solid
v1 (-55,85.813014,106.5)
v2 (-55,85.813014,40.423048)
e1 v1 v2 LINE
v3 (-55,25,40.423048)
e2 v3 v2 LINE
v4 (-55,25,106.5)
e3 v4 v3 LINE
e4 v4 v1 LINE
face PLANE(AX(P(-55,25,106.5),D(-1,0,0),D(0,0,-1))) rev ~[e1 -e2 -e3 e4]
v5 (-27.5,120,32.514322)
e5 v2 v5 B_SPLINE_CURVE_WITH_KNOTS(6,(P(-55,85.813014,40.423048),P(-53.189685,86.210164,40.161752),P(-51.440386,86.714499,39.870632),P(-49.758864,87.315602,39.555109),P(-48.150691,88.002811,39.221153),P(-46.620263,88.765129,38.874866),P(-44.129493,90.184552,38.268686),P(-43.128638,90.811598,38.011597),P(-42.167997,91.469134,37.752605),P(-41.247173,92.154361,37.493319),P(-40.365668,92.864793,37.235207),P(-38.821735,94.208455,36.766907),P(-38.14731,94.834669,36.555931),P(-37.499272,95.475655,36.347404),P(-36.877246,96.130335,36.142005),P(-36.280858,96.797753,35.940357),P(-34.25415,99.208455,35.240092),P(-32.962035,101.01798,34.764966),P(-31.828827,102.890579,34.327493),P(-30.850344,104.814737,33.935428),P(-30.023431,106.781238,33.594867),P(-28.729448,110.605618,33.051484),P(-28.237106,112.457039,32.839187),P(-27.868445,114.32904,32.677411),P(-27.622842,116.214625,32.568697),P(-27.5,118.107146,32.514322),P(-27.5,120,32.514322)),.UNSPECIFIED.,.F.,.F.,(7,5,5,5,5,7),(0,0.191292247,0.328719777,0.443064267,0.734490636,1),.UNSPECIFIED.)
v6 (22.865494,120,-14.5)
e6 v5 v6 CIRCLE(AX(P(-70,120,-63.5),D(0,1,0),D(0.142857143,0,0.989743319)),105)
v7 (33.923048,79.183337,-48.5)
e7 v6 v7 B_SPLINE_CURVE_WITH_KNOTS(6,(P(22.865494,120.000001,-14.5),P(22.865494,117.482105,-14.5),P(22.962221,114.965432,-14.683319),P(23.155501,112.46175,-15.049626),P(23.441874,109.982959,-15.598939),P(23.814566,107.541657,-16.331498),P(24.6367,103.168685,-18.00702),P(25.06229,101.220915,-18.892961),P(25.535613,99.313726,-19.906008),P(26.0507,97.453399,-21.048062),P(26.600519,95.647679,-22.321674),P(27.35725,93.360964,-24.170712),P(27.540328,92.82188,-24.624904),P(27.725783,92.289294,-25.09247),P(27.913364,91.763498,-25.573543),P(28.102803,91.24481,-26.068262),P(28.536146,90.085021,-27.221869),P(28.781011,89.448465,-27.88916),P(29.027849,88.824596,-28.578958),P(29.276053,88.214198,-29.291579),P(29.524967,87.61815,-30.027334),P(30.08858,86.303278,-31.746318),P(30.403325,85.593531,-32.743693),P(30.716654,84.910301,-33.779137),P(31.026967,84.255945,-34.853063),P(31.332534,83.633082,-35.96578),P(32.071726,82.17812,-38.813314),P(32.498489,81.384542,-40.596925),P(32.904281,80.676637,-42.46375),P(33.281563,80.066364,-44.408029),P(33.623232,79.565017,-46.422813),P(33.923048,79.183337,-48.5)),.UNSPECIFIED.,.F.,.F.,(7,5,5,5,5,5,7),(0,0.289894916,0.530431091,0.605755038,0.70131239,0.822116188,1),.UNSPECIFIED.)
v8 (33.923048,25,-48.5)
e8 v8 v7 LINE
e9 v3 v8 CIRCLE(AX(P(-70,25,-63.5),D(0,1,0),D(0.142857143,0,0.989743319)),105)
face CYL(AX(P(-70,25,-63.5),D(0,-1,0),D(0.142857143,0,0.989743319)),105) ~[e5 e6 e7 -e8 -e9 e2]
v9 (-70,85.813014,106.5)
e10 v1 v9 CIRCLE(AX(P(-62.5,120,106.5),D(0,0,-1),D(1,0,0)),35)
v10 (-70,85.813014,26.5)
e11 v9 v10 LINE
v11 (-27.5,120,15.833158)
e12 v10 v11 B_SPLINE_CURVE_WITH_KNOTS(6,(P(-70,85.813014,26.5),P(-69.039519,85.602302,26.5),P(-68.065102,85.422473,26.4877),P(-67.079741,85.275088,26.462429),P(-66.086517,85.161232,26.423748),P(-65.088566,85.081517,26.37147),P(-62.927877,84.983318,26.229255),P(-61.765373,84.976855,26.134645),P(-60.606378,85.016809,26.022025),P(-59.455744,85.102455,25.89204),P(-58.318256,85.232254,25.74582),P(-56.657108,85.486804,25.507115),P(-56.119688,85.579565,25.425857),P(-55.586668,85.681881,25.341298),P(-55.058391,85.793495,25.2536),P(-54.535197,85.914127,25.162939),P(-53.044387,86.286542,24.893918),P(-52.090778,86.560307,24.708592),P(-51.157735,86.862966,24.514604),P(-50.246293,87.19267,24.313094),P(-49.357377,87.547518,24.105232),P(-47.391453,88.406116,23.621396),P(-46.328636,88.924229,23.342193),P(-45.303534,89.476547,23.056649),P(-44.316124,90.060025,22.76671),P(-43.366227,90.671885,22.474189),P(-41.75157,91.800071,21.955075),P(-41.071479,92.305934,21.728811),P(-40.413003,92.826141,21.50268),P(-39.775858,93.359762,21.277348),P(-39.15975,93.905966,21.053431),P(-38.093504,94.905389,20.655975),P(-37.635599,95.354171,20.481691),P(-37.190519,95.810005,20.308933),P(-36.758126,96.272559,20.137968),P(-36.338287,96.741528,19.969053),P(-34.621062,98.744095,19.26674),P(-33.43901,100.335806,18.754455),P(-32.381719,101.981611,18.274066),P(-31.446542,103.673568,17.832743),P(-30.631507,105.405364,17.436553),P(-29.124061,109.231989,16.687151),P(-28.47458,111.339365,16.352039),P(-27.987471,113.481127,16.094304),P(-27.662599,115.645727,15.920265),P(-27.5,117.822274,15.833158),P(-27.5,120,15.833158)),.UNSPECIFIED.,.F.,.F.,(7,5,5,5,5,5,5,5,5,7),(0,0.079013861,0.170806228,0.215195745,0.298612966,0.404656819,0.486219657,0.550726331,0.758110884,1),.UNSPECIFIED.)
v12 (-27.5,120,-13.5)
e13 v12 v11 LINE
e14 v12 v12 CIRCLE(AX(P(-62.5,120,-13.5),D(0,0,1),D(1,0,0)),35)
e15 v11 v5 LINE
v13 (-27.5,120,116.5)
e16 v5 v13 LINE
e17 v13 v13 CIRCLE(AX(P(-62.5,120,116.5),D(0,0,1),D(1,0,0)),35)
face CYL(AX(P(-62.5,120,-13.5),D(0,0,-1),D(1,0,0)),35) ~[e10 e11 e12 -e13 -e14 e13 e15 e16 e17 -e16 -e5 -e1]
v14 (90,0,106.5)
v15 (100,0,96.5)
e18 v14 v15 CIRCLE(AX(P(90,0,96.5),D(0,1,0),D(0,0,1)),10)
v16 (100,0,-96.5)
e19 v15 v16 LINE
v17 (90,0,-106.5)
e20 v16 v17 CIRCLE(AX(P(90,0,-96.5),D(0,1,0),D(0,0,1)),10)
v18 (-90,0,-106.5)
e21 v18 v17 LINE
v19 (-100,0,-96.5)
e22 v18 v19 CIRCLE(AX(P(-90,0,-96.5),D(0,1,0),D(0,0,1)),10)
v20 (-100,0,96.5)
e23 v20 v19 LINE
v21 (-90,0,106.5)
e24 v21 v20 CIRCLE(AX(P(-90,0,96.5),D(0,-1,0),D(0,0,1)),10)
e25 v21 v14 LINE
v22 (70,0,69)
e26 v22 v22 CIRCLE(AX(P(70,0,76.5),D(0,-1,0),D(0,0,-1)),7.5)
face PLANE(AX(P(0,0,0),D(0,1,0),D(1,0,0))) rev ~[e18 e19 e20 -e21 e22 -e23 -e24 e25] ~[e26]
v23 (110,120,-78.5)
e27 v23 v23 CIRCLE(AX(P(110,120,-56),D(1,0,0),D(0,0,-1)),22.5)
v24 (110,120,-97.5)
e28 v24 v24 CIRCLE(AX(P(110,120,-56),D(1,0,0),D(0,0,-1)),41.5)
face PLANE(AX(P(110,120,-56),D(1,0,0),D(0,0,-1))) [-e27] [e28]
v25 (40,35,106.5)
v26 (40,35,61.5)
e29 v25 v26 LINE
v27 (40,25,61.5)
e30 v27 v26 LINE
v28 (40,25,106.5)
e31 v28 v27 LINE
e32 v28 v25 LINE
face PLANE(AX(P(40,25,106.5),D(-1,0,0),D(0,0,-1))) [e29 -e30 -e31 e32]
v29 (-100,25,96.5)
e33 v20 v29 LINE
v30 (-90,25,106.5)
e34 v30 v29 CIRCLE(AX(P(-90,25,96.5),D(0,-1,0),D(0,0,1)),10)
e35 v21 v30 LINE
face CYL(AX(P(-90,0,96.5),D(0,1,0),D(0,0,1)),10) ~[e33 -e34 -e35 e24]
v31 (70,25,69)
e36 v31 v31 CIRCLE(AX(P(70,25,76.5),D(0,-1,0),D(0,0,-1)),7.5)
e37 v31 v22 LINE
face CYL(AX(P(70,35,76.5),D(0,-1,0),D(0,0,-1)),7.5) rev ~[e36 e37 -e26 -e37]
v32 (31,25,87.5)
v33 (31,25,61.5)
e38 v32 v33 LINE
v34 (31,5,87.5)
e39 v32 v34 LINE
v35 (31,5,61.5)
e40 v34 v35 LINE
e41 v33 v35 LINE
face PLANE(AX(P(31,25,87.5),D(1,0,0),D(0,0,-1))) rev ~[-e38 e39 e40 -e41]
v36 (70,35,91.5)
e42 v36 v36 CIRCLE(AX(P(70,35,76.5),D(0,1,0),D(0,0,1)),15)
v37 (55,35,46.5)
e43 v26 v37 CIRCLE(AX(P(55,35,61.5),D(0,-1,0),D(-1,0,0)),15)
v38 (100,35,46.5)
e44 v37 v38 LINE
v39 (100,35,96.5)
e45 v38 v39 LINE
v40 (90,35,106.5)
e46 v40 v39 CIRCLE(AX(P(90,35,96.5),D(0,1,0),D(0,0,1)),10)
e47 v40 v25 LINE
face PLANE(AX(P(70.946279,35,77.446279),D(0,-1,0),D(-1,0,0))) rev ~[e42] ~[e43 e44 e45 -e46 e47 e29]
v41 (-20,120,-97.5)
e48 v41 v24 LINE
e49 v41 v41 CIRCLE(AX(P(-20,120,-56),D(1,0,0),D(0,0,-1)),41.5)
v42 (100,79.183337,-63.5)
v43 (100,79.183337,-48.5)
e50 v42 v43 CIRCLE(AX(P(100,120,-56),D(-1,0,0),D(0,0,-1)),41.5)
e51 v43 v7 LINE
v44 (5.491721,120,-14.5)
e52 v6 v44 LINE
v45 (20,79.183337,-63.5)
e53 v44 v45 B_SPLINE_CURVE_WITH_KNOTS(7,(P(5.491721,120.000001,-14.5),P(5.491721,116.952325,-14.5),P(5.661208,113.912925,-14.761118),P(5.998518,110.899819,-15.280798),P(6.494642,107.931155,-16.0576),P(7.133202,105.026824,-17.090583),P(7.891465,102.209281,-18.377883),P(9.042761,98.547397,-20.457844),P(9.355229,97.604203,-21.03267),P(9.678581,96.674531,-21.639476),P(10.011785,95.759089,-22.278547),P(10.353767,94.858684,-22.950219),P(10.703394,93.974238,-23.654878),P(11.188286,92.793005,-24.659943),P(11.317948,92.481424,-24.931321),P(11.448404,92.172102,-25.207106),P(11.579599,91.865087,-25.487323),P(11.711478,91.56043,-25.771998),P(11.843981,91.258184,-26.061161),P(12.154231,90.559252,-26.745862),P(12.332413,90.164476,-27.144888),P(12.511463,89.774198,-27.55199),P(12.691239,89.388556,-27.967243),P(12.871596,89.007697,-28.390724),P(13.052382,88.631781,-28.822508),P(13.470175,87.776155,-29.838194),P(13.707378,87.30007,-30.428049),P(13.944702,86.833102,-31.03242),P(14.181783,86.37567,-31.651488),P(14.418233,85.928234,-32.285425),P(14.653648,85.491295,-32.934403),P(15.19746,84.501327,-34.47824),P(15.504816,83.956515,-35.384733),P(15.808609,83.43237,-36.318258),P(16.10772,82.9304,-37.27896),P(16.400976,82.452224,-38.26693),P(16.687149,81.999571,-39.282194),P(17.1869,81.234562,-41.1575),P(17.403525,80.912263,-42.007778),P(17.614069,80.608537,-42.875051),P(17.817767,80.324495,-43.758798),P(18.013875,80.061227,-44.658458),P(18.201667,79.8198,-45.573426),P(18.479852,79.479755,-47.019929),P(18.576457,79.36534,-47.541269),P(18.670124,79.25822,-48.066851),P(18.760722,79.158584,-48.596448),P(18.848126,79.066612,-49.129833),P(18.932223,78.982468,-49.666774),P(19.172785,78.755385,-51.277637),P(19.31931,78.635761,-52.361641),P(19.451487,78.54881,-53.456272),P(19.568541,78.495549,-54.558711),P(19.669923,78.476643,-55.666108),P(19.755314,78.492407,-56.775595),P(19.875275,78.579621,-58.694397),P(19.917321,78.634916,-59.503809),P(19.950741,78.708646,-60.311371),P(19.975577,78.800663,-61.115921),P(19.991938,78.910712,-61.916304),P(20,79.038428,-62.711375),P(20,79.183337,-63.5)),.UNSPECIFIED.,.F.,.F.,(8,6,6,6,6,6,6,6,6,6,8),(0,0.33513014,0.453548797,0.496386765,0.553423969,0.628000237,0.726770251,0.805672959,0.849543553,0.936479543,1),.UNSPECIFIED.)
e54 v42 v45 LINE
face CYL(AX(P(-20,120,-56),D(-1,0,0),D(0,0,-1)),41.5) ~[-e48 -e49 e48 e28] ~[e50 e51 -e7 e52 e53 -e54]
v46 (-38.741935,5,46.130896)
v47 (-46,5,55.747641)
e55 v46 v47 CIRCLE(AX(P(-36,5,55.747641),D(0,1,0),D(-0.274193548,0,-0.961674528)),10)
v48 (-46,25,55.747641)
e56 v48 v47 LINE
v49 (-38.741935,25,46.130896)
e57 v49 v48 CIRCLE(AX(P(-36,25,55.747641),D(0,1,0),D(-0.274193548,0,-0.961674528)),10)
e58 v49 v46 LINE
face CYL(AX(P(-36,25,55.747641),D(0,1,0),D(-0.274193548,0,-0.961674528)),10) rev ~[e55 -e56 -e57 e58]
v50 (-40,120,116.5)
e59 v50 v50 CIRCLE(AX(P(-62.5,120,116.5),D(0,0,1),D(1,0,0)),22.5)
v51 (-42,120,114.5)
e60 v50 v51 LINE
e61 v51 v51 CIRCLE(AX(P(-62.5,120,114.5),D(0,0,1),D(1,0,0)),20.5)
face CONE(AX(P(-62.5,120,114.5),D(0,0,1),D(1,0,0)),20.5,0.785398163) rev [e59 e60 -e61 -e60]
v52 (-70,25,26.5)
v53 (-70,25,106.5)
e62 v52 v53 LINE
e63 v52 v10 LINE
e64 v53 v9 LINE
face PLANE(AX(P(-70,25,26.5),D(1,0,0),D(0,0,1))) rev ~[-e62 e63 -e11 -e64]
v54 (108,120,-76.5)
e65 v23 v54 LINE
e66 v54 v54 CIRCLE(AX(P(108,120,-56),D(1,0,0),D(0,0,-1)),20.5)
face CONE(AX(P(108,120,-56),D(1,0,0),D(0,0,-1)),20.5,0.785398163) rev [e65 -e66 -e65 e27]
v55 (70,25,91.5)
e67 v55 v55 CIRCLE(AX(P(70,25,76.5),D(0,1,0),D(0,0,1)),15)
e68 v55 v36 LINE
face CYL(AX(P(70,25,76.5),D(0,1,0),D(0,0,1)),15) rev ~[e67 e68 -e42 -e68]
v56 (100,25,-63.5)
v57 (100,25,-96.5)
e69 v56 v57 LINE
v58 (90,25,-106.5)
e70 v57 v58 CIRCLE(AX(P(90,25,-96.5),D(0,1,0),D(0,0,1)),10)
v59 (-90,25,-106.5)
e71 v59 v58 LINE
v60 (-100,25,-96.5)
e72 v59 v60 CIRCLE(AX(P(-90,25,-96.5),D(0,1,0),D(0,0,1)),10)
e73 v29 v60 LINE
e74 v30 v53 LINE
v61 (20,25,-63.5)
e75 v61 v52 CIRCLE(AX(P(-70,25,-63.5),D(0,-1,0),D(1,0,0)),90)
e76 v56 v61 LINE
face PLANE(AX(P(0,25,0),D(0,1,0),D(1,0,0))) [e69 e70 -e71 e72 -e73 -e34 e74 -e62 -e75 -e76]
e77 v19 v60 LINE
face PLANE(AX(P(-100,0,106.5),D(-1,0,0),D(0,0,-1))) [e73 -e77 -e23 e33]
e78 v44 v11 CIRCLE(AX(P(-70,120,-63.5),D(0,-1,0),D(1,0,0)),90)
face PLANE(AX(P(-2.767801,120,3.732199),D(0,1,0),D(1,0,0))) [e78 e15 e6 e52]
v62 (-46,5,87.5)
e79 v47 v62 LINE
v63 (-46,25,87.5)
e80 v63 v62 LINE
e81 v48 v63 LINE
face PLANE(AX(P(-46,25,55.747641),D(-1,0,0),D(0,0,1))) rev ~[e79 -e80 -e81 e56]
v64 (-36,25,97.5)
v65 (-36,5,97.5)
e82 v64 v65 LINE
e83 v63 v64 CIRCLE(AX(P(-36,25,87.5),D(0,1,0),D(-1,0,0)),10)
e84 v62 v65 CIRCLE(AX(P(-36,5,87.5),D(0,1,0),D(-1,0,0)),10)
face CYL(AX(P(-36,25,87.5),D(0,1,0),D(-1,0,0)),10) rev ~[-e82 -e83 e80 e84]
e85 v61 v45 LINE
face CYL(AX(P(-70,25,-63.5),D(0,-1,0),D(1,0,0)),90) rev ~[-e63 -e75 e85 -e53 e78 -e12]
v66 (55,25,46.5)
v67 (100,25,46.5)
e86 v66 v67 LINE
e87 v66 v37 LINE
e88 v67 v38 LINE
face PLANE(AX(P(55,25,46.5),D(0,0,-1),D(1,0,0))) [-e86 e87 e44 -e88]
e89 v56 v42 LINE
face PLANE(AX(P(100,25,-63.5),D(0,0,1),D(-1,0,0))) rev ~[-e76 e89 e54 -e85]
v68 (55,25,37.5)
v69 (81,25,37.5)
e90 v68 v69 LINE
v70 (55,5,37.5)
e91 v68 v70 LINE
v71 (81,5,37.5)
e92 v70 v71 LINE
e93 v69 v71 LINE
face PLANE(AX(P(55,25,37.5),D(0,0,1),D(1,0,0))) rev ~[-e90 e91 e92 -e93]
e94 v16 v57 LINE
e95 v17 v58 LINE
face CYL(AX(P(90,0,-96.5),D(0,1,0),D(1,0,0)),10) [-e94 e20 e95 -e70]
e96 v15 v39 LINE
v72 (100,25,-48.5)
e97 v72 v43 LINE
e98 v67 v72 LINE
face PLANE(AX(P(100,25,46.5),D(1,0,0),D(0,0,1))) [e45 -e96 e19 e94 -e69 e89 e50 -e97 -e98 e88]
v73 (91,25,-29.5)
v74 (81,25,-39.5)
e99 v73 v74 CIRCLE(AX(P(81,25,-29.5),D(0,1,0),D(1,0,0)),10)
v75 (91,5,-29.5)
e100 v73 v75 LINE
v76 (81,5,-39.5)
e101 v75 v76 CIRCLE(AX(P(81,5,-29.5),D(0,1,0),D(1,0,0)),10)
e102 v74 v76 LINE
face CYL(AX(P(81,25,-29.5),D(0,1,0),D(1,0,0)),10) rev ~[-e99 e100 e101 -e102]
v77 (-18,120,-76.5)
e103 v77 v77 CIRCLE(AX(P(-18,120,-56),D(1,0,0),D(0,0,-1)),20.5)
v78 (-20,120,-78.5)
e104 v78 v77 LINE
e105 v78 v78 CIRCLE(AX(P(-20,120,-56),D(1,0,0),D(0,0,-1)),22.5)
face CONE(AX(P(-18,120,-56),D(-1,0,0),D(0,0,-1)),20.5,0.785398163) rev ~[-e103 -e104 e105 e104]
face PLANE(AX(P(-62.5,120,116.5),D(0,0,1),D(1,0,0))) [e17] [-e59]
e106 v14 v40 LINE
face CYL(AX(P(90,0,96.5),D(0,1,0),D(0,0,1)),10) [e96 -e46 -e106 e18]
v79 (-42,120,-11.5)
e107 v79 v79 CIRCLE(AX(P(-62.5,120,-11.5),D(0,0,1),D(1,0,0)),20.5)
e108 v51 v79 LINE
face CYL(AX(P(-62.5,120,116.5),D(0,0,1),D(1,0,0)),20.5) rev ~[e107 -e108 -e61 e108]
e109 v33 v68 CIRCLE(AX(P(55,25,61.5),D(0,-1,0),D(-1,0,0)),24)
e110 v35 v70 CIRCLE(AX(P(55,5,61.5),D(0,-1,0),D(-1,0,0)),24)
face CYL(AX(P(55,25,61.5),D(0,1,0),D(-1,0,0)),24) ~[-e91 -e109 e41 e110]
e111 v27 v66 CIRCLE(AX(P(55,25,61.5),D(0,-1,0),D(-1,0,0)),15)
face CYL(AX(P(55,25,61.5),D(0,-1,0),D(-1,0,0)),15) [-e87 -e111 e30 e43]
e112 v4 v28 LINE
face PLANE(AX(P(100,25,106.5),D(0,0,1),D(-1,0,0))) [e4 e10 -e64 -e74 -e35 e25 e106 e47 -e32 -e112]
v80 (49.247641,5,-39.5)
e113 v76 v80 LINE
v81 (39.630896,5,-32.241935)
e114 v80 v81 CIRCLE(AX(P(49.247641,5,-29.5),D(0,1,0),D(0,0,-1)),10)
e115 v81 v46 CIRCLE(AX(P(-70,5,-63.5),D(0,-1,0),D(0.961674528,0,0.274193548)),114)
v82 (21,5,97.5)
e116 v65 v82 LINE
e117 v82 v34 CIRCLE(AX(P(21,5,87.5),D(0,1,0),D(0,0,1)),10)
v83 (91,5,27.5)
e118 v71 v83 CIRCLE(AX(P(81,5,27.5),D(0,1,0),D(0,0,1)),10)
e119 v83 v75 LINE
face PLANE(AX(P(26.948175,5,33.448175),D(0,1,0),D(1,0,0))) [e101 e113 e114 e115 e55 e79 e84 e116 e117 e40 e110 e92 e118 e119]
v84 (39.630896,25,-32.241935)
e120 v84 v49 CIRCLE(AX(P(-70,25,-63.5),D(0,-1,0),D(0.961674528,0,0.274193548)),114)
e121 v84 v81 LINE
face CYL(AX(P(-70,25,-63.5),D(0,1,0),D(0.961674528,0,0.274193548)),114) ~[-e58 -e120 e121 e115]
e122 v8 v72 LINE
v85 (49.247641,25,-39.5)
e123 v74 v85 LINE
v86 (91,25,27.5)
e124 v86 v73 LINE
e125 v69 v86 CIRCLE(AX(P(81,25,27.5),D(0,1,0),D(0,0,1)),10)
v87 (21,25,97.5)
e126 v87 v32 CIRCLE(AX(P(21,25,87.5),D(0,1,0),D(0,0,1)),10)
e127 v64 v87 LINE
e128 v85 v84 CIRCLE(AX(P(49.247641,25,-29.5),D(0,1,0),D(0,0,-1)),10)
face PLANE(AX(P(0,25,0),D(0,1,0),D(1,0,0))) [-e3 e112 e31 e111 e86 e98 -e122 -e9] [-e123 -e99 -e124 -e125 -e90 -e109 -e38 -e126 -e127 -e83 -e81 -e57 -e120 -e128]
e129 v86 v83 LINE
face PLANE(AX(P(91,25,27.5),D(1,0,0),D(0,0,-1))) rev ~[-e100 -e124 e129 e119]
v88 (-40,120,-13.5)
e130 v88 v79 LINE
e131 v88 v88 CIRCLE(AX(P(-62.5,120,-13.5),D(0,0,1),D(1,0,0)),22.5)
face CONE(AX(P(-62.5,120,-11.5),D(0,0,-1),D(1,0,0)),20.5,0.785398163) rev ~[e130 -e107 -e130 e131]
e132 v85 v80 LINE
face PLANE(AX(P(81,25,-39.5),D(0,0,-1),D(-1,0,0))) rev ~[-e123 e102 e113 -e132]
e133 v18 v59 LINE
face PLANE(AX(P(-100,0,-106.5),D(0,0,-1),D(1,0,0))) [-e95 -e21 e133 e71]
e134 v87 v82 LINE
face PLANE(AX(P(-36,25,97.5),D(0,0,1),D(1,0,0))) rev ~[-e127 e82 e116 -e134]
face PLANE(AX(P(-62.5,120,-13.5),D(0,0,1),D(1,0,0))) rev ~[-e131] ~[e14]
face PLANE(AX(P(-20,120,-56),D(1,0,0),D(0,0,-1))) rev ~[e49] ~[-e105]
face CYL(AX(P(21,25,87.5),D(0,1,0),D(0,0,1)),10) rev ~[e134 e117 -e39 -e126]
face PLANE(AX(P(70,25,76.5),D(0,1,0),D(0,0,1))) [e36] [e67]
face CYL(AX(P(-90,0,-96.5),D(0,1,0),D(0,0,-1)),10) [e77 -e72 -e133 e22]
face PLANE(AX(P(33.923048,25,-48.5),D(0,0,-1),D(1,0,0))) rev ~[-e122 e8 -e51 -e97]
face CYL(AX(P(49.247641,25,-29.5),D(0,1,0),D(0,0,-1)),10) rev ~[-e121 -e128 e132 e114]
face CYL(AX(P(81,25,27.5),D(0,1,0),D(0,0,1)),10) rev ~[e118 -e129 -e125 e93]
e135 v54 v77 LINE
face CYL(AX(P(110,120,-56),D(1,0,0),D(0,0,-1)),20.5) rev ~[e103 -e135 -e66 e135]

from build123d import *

# Parameters (mm, degrees)
BASE_PLATE_SKETCH_W                       = 200
BASE_PLATE_SKETCH_H                       = 213
BASE_PLATE_DEPTH                          = 25
BOLT_PAD_DEPTH                            = 10
BASE_PLATE_FILLETS_R10_R                  = 10
CENTRAL_HOUSING_DEPTH                     = 95
BEARING_BOSS_A_DEPTH                      = 10
BEARING_BOSS_A_DEPTH_BACK                 = 120
BEARING_BOSS_A_SKETCH_R                   = 35
BEARING_BOSS_B_DEPTH                      = 10
BEARING_BOSS_B_DEPTH_BACK                 = 120
BEARING_BOSS_B_SKETCH_R                   = 41.5
BEARING_BORE_A_41_REACH                   = 298.498
BEARING_BORE_A_SKETCH_R                   = 20.5
BEARING_BORE_B_41_REACH                   = 291.404
BEARING_BORE_B_SKETCH_R                   = 20.5
BORE_CHAMFERS_2X45_SIZE                   = 2
M8_COUNTERBORED_MOUNTING_HOLE_D           = 15
M8_COUNTERBORED_MOUNTING_HOLE_CBORE_D     = 30
M8_COUNTERBORED_MOUNTING_HOLE_CBORE_DEPTH = 10
BASE_POCKET_DEPTH                         = 20


with BuildPart() as part:
    # Base Plate Sketch → Base Plate (new body)
    with BuildSketch(Plane(origin=(0, 0, 0), x_dir=(1, 0, 0), z_dir=(0, 1, 0))):
        Rectangle(BASE_PLATE_SKETCH_W, BASE_PLATE_SKETCH_H)
    extrude(amount=BASE_PLATE_DEPTH)

    # Bolt Pad Sketch → Bolt Pad (add)
    with BuildSketch(Plane(origin=(0, 25, 0), x_dir=(1, 0, 0), z_dir=(0, 1, 0))):
        with BuildLine():
            Line((100, -106.5), (40, -106.5))
            Line((40, -106.5), (40, -61.5))
            ThreePointArc((40, -61.5), (44.393398282, -50.893398282), (55, -46.5))
            Line((55, -46.5), (100, -46.5))
            Line((100, -46.5), (100, -106.5))
        make_face()
    extrude(amount=BOLT_PAD_DEPTH)

    # Base Plate Fillets R10
    base_plate_fillets_r10_edges = [part.edges().sort_by_distance(p)[0] for p in [
        (100, 17.5, 106.5),
        (-100, 12.5, 106.5),
        (-100, 12.5, -106.5),
        (100, 12.5, -106.5),
    ]]
    fillet(base_plate_fillets_r10_edges, radius=BASE_PLATE_FILLETS_R10_R)

    # Central Housing Sketch → Central Housing (add)
    with BuildSketch(Plane(origin=(0, 25, 0), x_dir=(1, 0, 0), z_dir=(0, 1, 0))):
        with BuildLine():
            Line((100, 63.5), (20, 63.5))
            ThreePointArc((20, 63.5), (-6.360389693, -0.139610307), (-70, -26.5))
            Line((-70, -26.5), (-70, -106.5))
            Line((-70, -106.5), (-55, -106.5))
            Line((-55, -106.5), (-55, -40.423048454))
            ThreePointArc((-55, -40.423048454), (4.246212025, -10.746212025), (33.923048454, 48.5))
            Line((33.923048454, 48.5), (100, 48.5))
            Line((100, 48.5), (100, 63.5))
        make_face()
    extrude(amount=CENTRAL_HOUSING_DEPTH)

    # Bearing Boss A Sketch → Bearing Boss A (add, two sides: drawn at the far end of the back side and taken through both)
    with BuildSketch(Plane.XY.offset(106.5).offset(-BEARING_BOSS_A_DEPTH_BACK)):
        with Locations((-62.5, 120)):
            Circle(BEARING_BOSS_A_SKETCH_R)
    extrude(amount=BEARING_BOSS_A_DEPTH + BEARING_BOSS_A_DEPTH_BACK)

    # Bearing Boss B Sketch → Bearing Boss B (add, two sides: drawn at the far end of the back side and taken through both)
    with BuildSketch(Plane(origin=(100, 0, 0), x_dir=(0, 0, -1), z_dir=(1, 0, 0)).offset(-BEARING_BOSS_B_DEPTH_BACK)):
        with Locations((56, 120)):
            Circle(BEARING_BOSS_B_SKETCH_R)
    extrude(amount=BEARING_BOSS_B_DEPTH + BEARING_BOSS_B_DEPTH_BACK)

    # Bearing Bore A Sketch → Bearing Bore A Ø41 (cut, up to next)
    with BuildSketch(Plane.XY.offset(116.5), mode=Mode.PRIVATE) as bearing_bore_a_41_sk1:
        with Locations((-62.5, 120)):
            Circle(BEARING_BORE_A_SKETCH_R)
    bearing_bore_a_41_tool1 = extrude(bearing_bore_a_41_sk1.sketch, amount=-BEARING_BORE_A_41_REACH, mode=Mode.PRIVATE) & part.part
    add(bearing_bore_a_41_tool1.solids().sort_by_distance((-62.5, 120, 116.5))[0], mode=Mode.SUBTRACT)

    # Bearing Bore B Sketch → Bearing Bore B Ø41 (cut, up to next)
    with BuildSketch(Plane(origin=(110, 0, 0), x_dir=(0, 0, -1), z_dir=(1, 0, 0)), mode=Mode.PRIVATE) as bearing_bore_b_41_sk1:
        with Locations((56, 120)):
            Circle(BEARING_BORE_B_SKETCH_R)
    bearing_bore_b_41_tool1 = extrude(bearing_bore_b_41_sk1.sketch, amount=-BEARING_BORE_B_41_REACH, mode=Mode.PRIVATE) & part.part
    add(bearing_bore_b_41_tool1.solids().sort_by_distance((110, 120, -56))[0], mode=Mode.SUBTRACT)

    # Bore Chamfers 2x45°
    bore_chamfers_2x45_edges = [part.edges().sort_by_distance(p)[0] for p in [
        (-83, 120, 116.5),
        (-83, 120, -13.5),
        (110, 120, -35.5),
        (-20, 120, -35.5),
    ]]
    chamfer(bore_chamfers_2x45_edges, length=BORE_CHAMFERS_2X45_SIZE)

    # M8 Counterbored Mounting Hole (through all)
    with Locations(Plane(origin=(70, 35, 76.5), x_dir=(0, 0, 1), z_dir=(0, 1, 0))):
        with Locations((0, 0)):
            CounterBoreHole(M8_COUNTERBORED_MOUNTING_HOLE_D / 2, M8_COUNTERBORED_MOUNTING_HOLE_CBORE_D / 2, M8_COUNTERBORED_MOUNTING_HOLE_CBORE_DEPTH)

    # Base Pocket Sketch → Base Pocket (cut)
    with BuildSketch(Plane(origin=(0, 25, 0), x_dir=(1, 0, 0), z_dir=(0, 1, 0))):
        with BuildLine():
            Line((-46, -55.747641486), (-46, -87.5))
            ThreePointArc((-46, -87.5), (-43.071067812, -94.571067812), (-36, -97.5))
            Line((-36, -97.5), (21, -97.5))
            ThreePointArc((21, -97.5), (28.071067812, -94.571067812), (31, -87.5))
            Line((31, -87.5), (31, -61.5))
            ThreePointArc((31, -61.5), (38.029437252, -44.529437252), (55, -37.5))
            Line((55, -37.5), (81, -37.5))
            ThreePointArc((81, -37.5), (88.071067812, -34.571067812), (91, -27.5))
            Line((91, -27.5), (91, 29.5))
            ThreePointArc((91, 29.5), (88.071067812, 36.571067812), (81, 39.5))
            Line((81, 39.5), (49.247641486, 39.5))
            ThreePointArc((49.247641486, 39.5), (43.223496519, 37.481834214), (39.630896205, 32.241935484))
            ThreePointArc((39.630896205, 32.241935484), (10.610173055, -17.110173055), (-38.741935484, -46.130896205))
            ThreePointArc((-38.741935484, -46.130896205), (-43.981834214, -49.723496519), (-46, -55.747641486))
        make_face()
    extrude(amount=-BASE_POCKET_DEPTH, mode=Mode.SUBTRACT)


solid = part.part
